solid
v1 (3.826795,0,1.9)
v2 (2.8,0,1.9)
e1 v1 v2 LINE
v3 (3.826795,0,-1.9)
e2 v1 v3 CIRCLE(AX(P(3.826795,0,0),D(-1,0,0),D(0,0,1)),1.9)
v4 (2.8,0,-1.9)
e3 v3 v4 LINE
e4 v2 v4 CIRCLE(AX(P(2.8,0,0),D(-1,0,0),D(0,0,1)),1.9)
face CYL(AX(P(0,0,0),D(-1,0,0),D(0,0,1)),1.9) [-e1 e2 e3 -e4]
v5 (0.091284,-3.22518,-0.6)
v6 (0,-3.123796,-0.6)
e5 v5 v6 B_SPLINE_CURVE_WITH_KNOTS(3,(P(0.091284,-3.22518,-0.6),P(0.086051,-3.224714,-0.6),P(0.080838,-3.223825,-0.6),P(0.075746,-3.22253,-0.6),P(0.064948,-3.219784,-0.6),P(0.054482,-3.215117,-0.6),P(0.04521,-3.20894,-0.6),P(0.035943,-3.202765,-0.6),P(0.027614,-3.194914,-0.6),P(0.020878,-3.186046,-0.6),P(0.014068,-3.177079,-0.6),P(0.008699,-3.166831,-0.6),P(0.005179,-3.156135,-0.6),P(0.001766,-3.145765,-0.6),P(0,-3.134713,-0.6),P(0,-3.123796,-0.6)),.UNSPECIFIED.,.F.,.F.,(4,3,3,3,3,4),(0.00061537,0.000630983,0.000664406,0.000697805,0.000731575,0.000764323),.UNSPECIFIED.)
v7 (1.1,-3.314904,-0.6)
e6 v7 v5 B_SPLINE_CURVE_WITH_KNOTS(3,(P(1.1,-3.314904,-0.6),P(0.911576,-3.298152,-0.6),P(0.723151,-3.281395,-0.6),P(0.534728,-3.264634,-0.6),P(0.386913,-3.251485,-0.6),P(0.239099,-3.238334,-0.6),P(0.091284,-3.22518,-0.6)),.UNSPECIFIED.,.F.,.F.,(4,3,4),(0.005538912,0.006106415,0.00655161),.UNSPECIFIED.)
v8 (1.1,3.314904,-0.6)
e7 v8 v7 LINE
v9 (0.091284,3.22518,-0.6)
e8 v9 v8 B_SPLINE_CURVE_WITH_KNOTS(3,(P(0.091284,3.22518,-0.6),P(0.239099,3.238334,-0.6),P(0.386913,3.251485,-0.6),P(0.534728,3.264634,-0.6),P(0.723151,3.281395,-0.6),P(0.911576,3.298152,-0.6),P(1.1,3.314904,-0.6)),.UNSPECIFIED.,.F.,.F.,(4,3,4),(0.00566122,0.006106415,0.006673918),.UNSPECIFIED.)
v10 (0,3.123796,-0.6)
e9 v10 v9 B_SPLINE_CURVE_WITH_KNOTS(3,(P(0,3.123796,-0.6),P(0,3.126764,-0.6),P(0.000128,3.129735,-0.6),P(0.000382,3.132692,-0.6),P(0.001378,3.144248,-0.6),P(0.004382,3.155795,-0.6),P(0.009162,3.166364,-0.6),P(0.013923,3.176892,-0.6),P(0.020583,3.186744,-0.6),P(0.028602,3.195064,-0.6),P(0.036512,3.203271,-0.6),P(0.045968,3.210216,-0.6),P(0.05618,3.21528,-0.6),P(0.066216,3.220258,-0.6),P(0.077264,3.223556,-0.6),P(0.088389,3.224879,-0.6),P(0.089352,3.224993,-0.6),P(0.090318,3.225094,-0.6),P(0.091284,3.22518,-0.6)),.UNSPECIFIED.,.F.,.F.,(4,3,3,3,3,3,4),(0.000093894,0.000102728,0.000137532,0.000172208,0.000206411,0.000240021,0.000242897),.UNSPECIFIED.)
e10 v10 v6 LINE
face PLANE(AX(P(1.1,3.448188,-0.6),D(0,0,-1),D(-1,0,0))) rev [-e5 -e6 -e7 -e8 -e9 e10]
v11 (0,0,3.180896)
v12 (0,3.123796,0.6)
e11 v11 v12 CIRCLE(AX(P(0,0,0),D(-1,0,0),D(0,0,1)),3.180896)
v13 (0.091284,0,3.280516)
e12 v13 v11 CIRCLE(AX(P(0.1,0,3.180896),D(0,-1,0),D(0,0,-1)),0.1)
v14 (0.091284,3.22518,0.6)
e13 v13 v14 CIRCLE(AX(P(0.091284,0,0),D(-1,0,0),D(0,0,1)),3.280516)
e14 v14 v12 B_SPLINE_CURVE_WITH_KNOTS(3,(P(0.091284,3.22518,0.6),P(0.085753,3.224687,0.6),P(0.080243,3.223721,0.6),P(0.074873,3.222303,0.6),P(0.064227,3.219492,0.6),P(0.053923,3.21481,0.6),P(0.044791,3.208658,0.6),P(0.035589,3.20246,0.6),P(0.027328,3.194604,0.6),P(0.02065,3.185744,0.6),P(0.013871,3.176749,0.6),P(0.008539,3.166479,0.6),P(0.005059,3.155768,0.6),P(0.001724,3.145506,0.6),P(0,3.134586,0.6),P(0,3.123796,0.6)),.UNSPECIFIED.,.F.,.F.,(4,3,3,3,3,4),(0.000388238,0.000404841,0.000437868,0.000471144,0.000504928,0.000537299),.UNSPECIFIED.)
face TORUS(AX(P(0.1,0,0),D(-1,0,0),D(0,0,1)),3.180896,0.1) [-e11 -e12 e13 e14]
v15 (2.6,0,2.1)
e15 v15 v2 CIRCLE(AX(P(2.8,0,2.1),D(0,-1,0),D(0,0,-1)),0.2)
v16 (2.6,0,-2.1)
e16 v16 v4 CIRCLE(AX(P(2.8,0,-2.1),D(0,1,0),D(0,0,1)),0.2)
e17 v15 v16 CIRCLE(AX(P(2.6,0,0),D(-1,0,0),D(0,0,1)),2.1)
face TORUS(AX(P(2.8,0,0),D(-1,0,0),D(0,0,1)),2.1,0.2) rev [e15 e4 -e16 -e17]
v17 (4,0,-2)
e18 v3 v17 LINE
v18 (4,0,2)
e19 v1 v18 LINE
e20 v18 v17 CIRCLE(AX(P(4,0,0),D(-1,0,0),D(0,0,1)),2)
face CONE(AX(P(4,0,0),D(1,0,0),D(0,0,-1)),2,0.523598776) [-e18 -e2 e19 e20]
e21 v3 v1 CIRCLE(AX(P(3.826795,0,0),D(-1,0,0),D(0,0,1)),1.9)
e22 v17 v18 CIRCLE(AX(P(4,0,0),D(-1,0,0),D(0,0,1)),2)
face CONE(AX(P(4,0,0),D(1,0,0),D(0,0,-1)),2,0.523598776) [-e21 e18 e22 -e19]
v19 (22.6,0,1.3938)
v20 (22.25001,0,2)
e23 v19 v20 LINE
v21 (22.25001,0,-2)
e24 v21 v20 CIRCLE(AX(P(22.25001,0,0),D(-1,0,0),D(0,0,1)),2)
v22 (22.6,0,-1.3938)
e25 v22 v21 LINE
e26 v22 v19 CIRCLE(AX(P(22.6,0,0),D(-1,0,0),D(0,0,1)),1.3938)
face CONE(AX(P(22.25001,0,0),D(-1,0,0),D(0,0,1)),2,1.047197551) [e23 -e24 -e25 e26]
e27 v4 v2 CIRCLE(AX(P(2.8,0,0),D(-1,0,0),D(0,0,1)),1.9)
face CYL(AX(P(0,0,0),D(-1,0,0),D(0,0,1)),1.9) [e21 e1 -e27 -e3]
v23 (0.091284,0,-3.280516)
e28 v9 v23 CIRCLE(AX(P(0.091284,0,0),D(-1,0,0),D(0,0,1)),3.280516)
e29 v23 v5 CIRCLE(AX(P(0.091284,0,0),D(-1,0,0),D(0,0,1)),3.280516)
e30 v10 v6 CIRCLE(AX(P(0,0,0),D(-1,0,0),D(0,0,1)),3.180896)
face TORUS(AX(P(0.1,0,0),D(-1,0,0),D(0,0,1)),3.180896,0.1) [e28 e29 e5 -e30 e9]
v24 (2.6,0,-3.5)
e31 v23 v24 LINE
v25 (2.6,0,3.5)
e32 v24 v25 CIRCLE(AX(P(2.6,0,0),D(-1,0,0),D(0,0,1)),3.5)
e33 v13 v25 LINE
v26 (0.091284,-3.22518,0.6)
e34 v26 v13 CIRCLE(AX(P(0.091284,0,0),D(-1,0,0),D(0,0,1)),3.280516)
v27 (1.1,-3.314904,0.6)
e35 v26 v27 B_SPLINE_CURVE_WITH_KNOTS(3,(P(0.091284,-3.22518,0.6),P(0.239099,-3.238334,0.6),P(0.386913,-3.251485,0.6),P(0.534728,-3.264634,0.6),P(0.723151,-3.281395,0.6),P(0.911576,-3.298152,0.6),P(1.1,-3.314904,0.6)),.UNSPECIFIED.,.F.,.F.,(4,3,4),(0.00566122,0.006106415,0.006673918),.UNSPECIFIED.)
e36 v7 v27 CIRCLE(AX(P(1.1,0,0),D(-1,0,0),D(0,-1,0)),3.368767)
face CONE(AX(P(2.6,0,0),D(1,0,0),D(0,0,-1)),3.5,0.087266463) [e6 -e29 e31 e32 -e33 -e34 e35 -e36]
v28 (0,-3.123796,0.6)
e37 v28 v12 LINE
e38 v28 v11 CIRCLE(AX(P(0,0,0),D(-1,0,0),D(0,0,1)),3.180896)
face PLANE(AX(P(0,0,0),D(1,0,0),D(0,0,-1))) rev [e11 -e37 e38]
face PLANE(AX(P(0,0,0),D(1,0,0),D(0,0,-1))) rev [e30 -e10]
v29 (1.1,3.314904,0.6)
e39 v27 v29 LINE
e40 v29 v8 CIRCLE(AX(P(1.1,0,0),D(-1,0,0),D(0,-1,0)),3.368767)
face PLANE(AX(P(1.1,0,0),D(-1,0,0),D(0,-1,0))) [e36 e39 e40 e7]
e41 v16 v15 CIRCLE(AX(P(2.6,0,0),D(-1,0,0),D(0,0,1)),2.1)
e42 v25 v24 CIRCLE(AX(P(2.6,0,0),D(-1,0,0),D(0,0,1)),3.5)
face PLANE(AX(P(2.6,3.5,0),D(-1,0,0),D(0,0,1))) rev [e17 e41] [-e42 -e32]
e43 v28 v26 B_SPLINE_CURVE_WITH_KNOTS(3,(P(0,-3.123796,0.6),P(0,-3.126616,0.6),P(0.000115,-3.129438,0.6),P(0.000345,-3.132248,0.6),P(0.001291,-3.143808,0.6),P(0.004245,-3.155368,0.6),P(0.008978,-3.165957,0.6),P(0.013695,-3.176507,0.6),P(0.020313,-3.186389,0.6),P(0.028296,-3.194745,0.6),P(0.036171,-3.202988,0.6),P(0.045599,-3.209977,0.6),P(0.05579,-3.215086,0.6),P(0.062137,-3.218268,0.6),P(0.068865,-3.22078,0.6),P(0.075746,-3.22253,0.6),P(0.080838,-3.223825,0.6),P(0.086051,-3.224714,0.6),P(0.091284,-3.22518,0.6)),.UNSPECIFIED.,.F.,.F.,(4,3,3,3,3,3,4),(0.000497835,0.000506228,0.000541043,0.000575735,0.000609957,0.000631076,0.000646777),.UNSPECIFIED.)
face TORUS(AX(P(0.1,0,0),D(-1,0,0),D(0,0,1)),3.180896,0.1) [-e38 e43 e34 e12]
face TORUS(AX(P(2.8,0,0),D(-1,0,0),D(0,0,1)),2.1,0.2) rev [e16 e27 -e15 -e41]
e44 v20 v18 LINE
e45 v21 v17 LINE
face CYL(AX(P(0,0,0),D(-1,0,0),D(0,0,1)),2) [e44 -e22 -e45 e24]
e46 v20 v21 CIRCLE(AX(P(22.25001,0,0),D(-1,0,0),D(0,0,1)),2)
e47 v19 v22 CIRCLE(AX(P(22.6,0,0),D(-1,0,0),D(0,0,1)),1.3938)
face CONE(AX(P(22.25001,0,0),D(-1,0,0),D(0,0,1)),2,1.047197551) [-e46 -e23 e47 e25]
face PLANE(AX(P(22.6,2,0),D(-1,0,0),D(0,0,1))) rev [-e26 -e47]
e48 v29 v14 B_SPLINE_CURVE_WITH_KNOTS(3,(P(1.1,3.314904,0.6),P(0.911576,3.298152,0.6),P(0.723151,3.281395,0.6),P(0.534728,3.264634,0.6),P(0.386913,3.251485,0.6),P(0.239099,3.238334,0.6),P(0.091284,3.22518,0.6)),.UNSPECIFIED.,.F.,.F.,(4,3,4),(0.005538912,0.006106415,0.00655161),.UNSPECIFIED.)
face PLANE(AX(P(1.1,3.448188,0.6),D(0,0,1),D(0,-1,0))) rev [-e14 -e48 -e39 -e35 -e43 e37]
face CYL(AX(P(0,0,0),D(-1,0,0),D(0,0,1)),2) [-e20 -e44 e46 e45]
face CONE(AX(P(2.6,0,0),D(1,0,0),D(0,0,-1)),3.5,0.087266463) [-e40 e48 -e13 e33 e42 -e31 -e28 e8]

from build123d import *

# Parameters (mm, degrees)
CUT_EXTRUDE1_DEPTH = 1.1


with BuildPart() as part:
    # Sketch1 → Base-Revolve (revolve)
    with BuildSketch(Plane.XY, mode=Mode.PRIVATE) as base_revolve_sk:
        with BuildLine():
            Line((0, 0), (0, 3.180896357))
            ThreePointArc((0, 3.180896357), (0.026272266, 3.248455378), (0.091284426, 3.280515827))
            Line((0.091284426, 3.280515827), (2.6, 3.5))
            Line((2.6, 3.5), (2.6, 2.1))
            ThreePointArc((2.6, 2.1), (2.658578644, 1.958578644), (2.8, 1.9))
            Line((2.8, 1.9), (3.826794919, 1.9))
            Line((3.826794919, 1.9), (4, 2))
            Line((4, 2), (22.6, 2))
            Line((22.6, 2), (22.6, 0))
            Line((22.6, 0), (0, 0))
        make_face()
    revolve(base_revolve_sk.sketch.rotate(Axis((0, 0, 0), (1, 0, 0)), 90), axis=Axis((0, 0, 0), (1, 0, 0)))

    # Sketch2 → Cut-Extrude1 (cut)
    with BuildSketch(Plane.ZY):
        with BuildLine():
            Line((0.6, 3.44818793), (0.6, -3.44818793))
            ThreePointArc((0.6, -3.44818793), (0, -3.5), (-0.6, -3.44818793))
            Line((-0.6, -3.44818793), (-0.6, 3.44818793))
            ThreePointArc((-0.6, 3.44818793), (0, 3.5), (0.6, 3.44818793))
        make_face()
    extrude(amount=-CUT_EXTRUDE1_DEPTH, mode=Mode.SUBTRACT)

    # Sketch3 → Cut-Revolve1 (revolve, cut)
    with BuildSketch(Plane(origin=(0, 0, 0), x_dir=(1, 0, 0), z_dir=(0, 1, 0)), mode=Mode.PRIVATE) as cut_revolve1_sk:
        Polygon((22.250010267, 2), (22.949989733, 2), (22.6, 1.3938), align=None)
    revolve(cut_revolve1_sk.sketch.rotate(Axis((0, 0, 0), (1, 0, 0)), 180), axis=Axis((0, 0, 0), (1, 0, 0)), mode=Mode.SUBTRACT)


solid = part.part
